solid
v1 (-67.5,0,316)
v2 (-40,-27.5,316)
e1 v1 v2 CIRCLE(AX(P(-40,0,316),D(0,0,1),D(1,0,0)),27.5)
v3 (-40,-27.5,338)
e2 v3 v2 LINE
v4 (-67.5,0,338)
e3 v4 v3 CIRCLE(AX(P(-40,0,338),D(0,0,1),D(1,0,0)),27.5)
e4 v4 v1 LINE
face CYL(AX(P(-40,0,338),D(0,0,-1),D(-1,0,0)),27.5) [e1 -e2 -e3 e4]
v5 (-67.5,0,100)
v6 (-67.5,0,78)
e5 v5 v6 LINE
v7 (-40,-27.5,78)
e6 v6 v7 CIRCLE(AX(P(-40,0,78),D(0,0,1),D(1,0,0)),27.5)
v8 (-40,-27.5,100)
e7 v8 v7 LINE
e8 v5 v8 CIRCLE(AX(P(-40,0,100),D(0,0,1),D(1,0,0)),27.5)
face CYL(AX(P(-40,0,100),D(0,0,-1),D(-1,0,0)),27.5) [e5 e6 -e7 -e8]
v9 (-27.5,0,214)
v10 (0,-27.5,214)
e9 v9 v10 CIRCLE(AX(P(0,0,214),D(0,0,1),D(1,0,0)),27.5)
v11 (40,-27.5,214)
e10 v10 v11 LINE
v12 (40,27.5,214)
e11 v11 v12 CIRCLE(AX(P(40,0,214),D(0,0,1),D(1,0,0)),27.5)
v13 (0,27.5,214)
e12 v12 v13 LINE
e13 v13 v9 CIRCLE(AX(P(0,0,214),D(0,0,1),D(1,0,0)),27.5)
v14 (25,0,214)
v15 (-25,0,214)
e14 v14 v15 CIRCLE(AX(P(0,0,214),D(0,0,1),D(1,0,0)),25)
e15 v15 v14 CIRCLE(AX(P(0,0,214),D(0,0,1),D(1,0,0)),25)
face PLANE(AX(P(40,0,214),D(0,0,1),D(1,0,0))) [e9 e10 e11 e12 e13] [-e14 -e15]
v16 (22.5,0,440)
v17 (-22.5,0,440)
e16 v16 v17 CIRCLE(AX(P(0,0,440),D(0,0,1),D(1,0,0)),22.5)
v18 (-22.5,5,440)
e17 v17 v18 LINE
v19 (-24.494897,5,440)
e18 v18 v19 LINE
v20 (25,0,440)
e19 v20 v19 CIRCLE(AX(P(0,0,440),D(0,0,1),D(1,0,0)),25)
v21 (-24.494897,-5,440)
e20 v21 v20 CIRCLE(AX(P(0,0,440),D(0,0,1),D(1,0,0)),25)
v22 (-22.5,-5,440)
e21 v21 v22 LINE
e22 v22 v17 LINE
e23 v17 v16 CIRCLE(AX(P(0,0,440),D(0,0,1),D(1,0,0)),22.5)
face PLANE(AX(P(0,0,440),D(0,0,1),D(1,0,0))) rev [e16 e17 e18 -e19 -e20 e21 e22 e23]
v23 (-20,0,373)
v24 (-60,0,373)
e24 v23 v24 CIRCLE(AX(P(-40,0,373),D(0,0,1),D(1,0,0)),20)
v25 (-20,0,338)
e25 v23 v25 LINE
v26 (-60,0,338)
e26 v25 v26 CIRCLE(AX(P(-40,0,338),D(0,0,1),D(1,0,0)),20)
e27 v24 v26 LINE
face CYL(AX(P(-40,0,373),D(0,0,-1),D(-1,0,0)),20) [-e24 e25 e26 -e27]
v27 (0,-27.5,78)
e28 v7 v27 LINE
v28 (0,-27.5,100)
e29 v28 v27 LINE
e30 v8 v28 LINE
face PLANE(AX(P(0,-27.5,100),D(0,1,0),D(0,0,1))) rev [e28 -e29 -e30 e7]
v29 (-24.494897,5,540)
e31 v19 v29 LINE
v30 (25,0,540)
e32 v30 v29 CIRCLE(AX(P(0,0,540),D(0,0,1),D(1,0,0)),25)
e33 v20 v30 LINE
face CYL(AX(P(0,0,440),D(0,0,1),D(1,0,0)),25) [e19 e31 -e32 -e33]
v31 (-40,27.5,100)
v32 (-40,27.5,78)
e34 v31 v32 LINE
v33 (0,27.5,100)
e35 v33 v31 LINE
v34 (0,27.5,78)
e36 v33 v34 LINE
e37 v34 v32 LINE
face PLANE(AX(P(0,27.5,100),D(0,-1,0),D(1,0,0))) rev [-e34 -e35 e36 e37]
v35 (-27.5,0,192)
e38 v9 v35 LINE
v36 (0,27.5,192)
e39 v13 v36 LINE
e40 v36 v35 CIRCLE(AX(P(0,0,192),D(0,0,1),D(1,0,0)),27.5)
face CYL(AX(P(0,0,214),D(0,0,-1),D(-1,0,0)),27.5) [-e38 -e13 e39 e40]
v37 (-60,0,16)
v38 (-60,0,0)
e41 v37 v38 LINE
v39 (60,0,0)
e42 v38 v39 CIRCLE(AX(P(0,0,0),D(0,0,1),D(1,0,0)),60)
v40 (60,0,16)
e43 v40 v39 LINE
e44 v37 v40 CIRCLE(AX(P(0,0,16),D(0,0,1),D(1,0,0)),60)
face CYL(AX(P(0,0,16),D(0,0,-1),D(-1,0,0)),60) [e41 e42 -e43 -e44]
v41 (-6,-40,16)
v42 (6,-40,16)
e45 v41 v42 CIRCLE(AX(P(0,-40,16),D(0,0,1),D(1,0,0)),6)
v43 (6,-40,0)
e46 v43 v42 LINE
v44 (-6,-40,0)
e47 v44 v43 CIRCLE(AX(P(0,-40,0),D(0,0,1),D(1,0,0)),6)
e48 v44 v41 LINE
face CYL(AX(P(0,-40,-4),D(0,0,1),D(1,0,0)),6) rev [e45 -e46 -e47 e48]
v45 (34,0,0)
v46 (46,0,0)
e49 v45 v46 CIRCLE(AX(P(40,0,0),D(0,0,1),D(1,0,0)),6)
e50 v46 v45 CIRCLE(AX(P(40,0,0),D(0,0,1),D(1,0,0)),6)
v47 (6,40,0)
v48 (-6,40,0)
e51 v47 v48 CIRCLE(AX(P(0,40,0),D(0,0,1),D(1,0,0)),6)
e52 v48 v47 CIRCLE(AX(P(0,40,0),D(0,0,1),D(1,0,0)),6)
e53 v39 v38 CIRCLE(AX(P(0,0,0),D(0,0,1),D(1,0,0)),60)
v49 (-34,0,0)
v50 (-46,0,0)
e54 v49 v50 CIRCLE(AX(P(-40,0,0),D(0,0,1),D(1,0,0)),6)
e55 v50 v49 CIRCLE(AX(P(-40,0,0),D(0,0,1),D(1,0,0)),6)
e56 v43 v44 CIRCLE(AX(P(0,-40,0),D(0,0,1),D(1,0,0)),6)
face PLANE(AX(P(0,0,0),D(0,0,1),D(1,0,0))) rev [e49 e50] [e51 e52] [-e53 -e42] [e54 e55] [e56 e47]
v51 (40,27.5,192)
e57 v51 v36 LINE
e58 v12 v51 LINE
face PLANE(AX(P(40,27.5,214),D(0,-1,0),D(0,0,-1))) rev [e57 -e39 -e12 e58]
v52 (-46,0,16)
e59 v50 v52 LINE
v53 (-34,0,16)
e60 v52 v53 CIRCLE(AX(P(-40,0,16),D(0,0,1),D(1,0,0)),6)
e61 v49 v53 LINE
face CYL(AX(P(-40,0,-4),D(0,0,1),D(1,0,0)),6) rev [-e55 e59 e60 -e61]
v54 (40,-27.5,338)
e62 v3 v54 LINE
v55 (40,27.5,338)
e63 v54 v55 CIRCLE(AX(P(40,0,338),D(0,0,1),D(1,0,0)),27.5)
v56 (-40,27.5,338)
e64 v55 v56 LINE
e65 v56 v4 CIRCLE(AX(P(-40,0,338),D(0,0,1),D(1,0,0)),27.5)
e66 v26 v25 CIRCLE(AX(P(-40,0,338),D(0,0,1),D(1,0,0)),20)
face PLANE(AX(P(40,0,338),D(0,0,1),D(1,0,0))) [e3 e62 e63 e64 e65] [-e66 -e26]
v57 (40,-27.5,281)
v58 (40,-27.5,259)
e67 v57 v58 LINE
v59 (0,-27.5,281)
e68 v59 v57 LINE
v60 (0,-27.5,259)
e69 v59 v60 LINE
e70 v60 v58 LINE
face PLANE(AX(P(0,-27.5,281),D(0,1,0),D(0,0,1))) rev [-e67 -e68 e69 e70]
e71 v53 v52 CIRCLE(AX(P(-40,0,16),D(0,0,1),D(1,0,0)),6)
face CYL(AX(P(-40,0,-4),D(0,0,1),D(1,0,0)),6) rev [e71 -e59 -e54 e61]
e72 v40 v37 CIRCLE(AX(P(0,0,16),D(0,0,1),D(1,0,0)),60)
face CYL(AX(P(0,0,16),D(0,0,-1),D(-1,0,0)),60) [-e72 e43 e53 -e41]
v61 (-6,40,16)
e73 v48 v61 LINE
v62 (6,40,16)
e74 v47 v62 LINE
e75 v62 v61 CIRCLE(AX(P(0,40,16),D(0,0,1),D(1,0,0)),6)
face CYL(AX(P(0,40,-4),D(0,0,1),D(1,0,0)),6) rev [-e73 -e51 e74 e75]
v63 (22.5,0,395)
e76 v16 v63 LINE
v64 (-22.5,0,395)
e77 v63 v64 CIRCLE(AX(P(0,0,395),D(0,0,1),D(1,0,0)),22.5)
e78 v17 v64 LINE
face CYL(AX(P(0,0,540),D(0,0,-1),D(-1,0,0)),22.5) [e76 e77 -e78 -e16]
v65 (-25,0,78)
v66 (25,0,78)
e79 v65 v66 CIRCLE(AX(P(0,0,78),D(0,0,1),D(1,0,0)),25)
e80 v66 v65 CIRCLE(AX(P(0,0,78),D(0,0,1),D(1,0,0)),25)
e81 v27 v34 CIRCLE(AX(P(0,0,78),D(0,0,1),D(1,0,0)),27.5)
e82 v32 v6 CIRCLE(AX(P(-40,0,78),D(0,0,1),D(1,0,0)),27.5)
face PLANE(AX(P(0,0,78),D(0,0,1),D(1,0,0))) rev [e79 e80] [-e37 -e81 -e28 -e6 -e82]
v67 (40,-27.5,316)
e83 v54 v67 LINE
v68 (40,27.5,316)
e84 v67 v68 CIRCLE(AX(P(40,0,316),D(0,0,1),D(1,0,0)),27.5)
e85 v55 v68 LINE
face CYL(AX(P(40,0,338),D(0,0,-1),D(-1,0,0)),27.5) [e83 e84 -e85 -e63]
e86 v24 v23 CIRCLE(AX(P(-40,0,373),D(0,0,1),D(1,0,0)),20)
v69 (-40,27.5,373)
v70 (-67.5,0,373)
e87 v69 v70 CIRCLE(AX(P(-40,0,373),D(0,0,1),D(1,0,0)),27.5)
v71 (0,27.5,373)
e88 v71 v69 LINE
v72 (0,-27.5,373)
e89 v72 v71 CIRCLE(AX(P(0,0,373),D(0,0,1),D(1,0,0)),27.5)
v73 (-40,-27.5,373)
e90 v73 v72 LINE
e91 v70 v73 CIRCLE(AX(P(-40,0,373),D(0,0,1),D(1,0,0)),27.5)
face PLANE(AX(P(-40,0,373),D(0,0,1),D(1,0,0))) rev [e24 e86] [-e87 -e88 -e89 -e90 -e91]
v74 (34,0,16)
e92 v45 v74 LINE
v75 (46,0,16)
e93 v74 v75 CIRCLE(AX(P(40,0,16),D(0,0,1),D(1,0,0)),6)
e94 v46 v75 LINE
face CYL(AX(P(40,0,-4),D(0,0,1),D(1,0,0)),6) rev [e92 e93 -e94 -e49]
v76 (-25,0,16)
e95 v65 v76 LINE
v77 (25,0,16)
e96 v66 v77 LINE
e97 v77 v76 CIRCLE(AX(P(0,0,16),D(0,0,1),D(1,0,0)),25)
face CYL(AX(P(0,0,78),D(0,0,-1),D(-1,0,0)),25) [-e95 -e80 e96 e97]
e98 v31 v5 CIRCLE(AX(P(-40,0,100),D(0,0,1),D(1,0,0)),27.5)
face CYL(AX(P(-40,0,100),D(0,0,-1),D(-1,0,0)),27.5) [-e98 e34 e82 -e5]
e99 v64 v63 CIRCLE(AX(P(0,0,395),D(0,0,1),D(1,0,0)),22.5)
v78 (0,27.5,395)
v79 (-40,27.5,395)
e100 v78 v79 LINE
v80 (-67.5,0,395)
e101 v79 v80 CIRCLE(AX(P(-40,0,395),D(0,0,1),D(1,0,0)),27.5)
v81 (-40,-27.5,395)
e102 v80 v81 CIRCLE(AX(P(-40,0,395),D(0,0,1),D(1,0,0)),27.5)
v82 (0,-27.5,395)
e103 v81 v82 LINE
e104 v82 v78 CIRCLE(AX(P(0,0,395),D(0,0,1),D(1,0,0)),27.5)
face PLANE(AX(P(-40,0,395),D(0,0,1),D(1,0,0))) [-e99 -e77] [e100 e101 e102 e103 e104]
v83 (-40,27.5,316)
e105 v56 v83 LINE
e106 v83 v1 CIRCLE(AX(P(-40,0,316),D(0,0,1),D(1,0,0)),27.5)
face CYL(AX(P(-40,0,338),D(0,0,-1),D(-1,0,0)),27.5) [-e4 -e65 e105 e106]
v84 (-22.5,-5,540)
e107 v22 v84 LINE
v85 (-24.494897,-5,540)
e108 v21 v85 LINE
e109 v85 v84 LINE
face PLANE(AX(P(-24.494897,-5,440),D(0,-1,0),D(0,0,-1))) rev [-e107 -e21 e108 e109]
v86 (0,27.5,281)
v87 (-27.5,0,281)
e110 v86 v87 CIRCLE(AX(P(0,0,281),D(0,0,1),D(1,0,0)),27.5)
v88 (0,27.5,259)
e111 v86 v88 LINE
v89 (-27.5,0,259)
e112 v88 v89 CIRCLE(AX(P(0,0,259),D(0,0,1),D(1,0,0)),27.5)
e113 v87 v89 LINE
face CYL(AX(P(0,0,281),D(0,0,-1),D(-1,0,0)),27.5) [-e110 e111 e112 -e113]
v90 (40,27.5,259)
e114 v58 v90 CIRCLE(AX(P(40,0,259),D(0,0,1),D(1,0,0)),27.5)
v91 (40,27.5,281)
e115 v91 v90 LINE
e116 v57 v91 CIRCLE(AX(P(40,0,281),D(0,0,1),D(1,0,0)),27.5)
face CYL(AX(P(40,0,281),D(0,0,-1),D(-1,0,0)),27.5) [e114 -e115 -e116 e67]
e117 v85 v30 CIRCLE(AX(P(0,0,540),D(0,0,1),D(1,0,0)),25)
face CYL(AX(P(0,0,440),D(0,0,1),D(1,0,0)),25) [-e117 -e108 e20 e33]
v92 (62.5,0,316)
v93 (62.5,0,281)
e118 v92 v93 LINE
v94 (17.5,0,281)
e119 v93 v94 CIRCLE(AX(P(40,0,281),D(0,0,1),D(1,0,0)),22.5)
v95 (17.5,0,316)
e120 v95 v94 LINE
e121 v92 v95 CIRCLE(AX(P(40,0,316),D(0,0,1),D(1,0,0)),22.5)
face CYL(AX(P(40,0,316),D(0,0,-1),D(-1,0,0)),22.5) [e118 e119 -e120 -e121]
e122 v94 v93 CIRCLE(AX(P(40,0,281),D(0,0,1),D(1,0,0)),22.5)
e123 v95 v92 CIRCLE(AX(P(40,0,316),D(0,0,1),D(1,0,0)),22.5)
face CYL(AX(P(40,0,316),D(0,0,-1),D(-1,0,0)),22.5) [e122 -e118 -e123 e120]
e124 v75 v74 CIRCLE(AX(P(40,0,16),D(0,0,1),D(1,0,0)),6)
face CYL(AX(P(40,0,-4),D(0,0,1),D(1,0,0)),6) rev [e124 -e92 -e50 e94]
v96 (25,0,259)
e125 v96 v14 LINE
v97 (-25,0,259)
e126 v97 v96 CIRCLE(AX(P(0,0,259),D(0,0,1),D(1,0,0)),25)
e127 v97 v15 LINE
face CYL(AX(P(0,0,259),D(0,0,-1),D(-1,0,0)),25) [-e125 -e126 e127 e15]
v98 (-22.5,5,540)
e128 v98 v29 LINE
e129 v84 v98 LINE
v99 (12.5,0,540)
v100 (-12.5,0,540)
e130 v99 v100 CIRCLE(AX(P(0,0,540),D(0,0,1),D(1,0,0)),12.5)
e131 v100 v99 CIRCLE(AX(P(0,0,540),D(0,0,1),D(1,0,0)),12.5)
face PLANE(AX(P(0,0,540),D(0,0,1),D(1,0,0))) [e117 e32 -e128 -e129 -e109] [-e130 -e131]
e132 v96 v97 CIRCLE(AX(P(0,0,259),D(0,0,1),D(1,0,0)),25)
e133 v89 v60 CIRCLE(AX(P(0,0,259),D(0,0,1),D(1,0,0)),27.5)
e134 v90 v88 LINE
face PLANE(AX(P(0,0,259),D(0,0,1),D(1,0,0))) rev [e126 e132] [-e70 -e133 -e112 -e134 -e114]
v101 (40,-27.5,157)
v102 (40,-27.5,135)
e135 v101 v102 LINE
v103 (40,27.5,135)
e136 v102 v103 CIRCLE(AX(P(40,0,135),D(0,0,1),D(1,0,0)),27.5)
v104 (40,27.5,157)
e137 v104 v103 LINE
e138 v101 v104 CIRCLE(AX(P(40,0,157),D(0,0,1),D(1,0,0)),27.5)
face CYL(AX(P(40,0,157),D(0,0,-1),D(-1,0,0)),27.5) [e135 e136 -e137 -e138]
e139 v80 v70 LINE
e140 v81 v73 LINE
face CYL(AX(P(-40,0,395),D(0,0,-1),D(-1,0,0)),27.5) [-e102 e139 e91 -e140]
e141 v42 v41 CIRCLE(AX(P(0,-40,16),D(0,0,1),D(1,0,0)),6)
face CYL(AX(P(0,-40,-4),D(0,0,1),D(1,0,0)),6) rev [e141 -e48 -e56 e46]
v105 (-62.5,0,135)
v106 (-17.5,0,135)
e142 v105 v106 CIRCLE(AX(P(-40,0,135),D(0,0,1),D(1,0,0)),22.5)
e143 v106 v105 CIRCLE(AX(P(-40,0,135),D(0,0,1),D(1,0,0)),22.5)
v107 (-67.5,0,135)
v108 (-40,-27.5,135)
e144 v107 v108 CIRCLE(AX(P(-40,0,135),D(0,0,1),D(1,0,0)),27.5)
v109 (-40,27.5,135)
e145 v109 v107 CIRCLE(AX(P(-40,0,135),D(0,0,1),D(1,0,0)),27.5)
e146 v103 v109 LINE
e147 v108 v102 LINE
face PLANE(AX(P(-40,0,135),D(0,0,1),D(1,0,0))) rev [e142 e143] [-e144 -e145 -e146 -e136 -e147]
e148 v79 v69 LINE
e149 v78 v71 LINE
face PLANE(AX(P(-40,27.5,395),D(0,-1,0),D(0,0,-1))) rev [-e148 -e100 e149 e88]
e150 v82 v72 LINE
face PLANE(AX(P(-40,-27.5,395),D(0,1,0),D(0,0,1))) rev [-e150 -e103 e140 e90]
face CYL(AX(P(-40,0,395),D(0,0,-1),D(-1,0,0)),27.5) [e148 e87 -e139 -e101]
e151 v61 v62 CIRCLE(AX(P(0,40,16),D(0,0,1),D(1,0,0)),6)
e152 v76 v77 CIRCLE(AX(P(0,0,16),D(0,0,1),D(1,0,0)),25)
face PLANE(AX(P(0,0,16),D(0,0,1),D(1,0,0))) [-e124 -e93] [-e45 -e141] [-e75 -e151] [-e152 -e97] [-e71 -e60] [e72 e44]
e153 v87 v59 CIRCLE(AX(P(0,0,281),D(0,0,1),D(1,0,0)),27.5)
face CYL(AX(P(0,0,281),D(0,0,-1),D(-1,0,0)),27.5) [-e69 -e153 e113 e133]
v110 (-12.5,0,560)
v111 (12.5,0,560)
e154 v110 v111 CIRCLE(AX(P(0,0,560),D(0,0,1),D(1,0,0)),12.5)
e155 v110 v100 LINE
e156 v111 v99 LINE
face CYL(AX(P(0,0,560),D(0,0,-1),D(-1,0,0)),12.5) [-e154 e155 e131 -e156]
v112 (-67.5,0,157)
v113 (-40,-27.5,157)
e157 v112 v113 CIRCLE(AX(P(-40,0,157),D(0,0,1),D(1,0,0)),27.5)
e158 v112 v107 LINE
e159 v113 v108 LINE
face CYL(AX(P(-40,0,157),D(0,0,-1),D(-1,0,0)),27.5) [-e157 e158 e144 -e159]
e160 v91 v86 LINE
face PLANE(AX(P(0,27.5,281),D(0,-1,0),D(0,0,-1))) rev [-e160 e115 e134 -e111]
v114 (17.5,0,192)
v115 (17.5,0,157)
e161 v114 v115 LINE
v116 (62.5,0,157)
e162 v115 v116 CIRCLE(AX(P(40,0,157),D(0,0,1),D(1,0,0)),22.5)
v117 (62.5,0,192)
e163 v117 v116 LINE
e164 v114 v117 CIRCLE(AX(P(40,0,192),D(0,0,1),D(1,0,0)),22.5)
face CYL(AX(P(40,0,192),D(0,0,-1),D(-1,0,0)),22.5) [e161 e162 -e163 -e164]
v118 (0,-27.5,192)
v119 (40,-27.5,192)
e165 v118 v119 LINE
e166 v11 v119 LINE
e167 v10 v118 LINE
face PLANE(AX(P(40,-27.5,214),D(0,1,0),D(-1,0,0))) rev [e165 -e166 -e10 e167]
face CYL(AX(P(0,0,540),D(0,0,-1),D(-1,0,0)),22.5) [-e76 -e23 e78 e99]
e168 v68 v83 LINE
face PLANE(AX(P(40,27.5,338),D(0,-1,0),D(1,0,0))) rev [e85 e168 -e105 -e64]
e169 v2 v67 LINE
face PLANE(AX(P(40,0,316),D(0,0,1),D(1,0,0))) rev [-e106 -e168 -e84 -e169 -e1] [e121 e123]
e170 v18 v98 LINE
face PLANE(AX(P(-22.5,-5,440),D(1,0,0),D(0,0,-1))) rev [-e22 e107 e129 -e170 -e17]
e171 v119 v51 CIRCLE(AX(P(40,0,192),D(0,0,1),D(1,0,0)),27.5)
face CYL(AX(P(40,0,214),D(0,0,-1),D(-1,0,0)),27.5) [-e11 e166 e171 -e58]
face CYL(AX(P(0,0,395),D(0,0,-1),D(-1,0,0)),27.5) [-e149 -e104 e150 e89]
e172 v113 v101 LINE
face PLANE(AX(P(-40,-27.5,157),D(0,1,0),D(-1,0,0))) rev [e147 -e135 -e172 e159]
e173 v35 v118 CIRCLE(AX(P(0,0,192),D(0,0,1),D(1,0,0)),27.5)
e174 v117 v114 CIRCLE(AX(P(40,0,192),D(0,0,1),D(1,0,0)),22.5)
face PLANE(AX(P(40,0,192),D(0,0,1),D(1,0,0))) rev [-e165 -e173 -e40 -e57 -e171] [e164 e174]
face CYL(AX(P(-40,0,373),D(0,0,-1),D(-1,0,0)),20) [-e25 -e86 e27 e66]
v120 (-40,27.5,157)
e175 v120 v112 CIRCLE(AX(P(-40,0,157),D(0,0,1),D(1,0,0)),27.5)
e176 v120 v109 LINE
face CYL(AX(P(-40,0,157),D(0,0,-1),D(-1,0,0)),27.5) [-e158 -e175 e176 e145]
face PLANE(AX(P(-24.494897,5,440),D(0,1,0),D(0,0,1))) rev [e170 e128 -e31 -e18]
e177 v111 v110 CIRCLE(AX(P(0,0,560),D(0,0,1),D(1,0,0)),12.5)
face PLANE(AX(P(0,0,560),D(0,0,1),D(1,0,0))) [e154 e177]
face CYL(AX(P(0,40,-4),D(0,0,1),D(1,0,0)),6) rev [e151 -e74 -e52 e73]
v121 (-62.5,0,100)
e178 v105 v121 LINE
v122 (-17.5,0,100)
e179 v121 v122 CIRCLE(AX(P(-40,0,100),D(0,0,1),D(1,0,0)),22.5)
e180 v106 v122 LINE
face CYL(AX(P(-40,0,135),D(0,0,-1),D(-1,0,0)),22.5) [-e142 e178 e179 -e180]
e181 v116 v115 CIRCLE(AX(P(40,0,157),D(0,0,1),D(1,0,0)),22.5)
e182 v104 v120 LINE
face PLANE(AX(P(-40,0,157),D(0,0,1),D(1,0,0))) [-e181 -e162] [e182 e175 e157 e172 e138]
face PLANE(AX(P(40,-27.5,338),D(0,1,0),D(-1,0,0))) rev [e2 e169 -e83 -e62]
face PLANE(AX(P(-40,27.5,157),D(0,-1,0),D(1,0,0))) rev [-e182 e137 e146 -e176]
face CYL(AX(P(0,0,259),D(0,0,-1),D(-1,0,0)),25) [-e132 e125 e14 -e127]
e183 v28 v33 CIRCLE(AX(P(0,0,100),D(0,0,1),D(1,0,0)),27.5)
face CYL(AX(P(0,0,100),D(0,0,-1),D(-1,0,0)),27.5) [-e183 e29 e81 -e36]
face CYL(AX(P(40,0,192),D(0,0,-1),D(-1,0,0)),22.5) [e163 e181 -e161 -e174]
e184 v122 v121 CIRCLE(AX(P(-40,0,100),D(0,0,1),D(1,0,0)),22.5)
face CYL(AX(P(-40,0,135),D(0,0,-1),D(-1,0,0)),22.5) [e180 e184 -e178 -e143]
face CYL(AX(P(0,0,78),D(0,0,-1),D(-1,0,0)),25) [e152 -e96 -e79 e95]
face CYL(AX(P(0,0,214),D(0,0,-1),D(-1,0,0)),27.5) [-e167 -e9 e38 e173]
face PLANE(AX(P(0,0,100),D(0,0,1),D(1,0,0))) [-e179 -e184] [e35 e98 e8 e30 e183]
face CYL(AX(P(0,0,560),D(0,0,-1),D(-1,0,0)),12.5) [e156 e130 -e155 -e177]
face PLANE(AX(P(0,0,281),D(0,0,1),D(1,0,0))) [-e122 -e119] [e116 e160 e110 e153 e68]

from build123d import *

# Parameters (mm, degrees)
FLANGE_SKETCH_R               = 60
FLANGE_120X16_DEPTH           = 16
FRONT_SHAFT_SKETCH_R          = 25
FRONT_SHAFT_50X62_DEPTH       = 62
CRANK_WEB_1_DEPTH             = 22
CRANKPIN_1_SKETCH_R           = 22.5
CRANKPIN_1_45_DEPTH           = 35
CRANK_WEB_2_DEPTH             = 22
CRANKPIN_2_SKETCH_R           = 22.5
CRANKPIN_2_45_DEPTH           = 35
CRANK_WEB_3_DEPTH             = 22
CENTRE_MAIN_JOURNAL_SKETCH_R  = 25
CENTRE_MAIN_JOURNAL_50_DEPTH  = 45
CRANK_WEB_4_DEPTH             = 22
CRANKPIN_3_SKETCH_R           = 22.5
CRANKPIN_3_45_DEPTH           = 35
CRANK_WEB_5_DEPTH             = 22
CRANKPIN_4_SKETCH_R           = 20
CRANKPIN_4_40_DEPTH           = 35
CRANK_WEB_6_DEPTH             = 22
REAR_SHAFT_SKETCH_R           = 22.5
REAR_SHAFT_45X145_DEPTH       = 145
REAR_START                    = -100
REAR_SHAFT_STEP_SKETCH_R      = 25
REAR_SHAFT_STEP_50X100_DEPTH  = 100
REAR_SHAFT_PROFILE_CUT_DEPTH  = 100
END_STUB_SKETCH_R             = 12.5
END_STUB_25X20_DEPTH          = 20
FLANGE_BOLT_HOLES_SKETCH_R    = 6
FLANGE_BOLT_HOLES_4X_12_DEPTH = 20


with BuildPart() as part:
    # Flange Sketch → Flange Ø120x16 (new body)
    with BuildSketch(Plane.XY):
        Circle(FLANGE_SKETCH_R)
    extrude(amount=FLANGE_120X16_DEPTH)

    # Front Shaft Sketch → Front Shaft Ø50x62 (add)
    with BuildSketch(Plane.XY.offset(16)):
        Circle(FRONT_SHAFT_SKETCH_R)
    extrude(amount=FRONT_SHAFT_50X62_DEPTH)

    # Crank Web 1 Sketch → Crank Web 1 (add)
    with BuildSketch(Plane.XY.offset(78)):
        with BuildLine():
            Line((0, -27.5), (-40, -27.5))
            ThreePointArc((-40, -27.5), (-67.5, 0), (-40, 27.5))
            Line((-40, 27.5), (0, 27.5))
            ThreePointArc((0, 27.5), (27.5, 0), (0, -27.5))
        make_face()
    extrude(amount=CRANK_WEB_1_DEPTH)

    # Crankpin 1 Sketch → Crankpin 1 Ø45 (add)
    with BuildSketch(Plane.XY.offset(100)):
        with Locations((-40, 0)):
            Circle(CRANKPIN_1_SKETCH_R)
    extrude(amount=CRANKPIN_1_45_DEPTH)

    # Crank Web 2 Sketch → Crank Web 2 (add)
    with BuildSketch(Plane.XY.offset(135)):
        with BuildLine():
            Line((-40, 27.5), (40, 27.5))
            ThreePointArc((40, 27.5), (67.5, 0), (40, -27.5))
            Line((40, -27.5), (-40, -27.5))
            ThreePointArc((-40, -27.5), (-67.5, 0), (-40, 27.5))
        make_face()
    extrude(amount=CRANK_WEB_2_DEPTH)

    # Crankpin 2 Sketch → Crankpin 2 Ø45 (add)
    with BuildSketch(Plane.XY.offset(157)):
        with Locations((40, 0)):
            Circle(CRANKPIN_2_SKETCH_R)
    extrude(amount=CRANKPIN_2_45_DEPTH)

    # Crank Web 3 Sketch → Crank Web 3 (add)
    with BuildSketch(Plane.XY.offset(192)):
        with BuildLine():
            Line((40, -27.5), (0, -27.5))
            ThreePointArc((0, -27.5), (-27.5, 0), (0, 27.5))
            Line((0, 27.5), (40, 27.5))
            ThreePointArc((40, 27.5), (67.5, 0), (40, -27.5))
        make_face()
    extrude(amount=CRANK_WEB_3_DEPTH)

    # Centre Main Journal Sketch → Centre Main Journal Ø50 (add)
    with BuildSketch(Plane.XY.offset(214)):
        Circle(CENTRE_MAIN_JOURNAL_SKETCH_R)
    extrude(amount=CENTRE_MAIN_JOURNAL_50_DEPTH)

    # Crank Web 4 Sketch → Crank Web 4 (add)
    with BuildSketch(Plane.XY.offset(259)):
        with BuildLine():
            Line((0, 27.5), (40, 27.5))
            ThreePointArc((40, 27.5), (67.5, 0), (40, -27.5))
            Line((40, -27.5), (0, -27.5))
            ThreePointArc((0, -27.5), (-27.5, 0), (0, 27.5))
        make_face()
    extrude(amount=CRANK_WEB_4_DEPTH)

    # Crankpin 3 Sketch → Crankpin 3 Ø45 (add)
    with BuildSketch(Plane.XY.offset(281)):
        with Locations((40, 0)):
            Circle(CRANKPIN_3_SKETCH_R)
    extrude(amount=CRANKPIN_3_45_DEPTH)

    # Crank Web 5 Sketch → Crank Web 5 (add)
    with BuildSketch(Plane.XY.offset(316)):
        with BuildLine():
            Line((40, -27.5), (-40, -27.5))
            ThreePointArc((-40, -27.5), (-67.5, 0), (-40, 27.5))
            Line((-40, 27.5), (40, 27.5))
            ThreePointArc((40, 27.5), (67.5, 0), (40, -27.5))
        make_face()
    extrude(amount=CRANK_WEB_5_DEPTH)

    # Crankpin 4 Sketch → Crankpin 4 Ø40 (add)
    with BuildSketch(Plane.XY.offset(338)):
        with Locations((-40, 0)):
            Circle(CRANKPIN_4_SKETCH_R)
    extrude(amount=CRANKPIN_4_40_DEPTH)

    # Crank Web 6 Sketch → Crank Web 6 (add)
    with BuildSketch(Plane.XY.offset(373)):
        with BuildLine():
            Line((-40, 27.5), (0, 27.5))
            ThreePointArc((0, 27.5), (27.5, 0), (0, -27.5))
            Line((0, -27.5), (-40, -27.5))
            ThreePointArc((-40, -27.5), (-67.5, 0), (-40, 27.5))
        make_face()
    extrude(amount=CRANK_WEB_6_DEPTH)

    # Rear Shaft Sketch → Rear Shaft Ø45x145 (add)
    with BuildSketch(Plane.XY.offset(395)):
        Circle(REAR_SHAFT_SKETCH_R)
    extrude(amount=REAR_SHAFT_45X145_DEPTH)

    # Rear Shaft Step Sketch → Rear Shaft Step Ø50x100 (add)
    with BuildSketch(Plane.XY.offset(540).offset(REAR_START)):
        Circle(REAR_SHAFT_STEP_SKETCH_R)
    extrude(amount=REAR_SHAFT_STEP_50X100_DEPTH)

    # Rear Shaft Cut Sketch → Rear Shaft Profile Cut (cut)
    with BuildSketch(Plane.XY.offset(540).offset(REAR_START)):
        with BuildLine():
            Line((-24.494897428, -5), (-22.5, -5))
            Line((-22.5, -5), (-22.5, 5))
            Line((-22.5, 5), (-24.494897428, 5))
            ThreePointArc((-24.494897428, 5), (-25, 0), (-24.494897428, -5))
        make_face()
    extrude(amount=REAR_SHAFT_PROFILE_CUT_DEPTH, mode=Mode.SUBTRACT)

    # End Stub Sketch → End Stub Ø25x20 (add)
    with BuildSketch(Plane.XY.offset(540)):
        Circle(END_STUB_SKETCH_R)
    extrude(amount=END_STUB_25X20_DEPTH)

    # Flange Bolt Holes Sketch → Flange Bolt Holes 4xØ12 (cut)
    with BuildSketch(Plane.XY.offset(16)):
        with Locations((0, 40)):
            Circle(FLANGE_BOLT_HOLES_SKETCH_R)
        with Locations((0, -40)):
            Circle(FLANGE_BOLT_HOLES_SKETCH_R)
        with Locations((-40, 0)):
            Circle(FLANGE_BOLT_HOLES_SKETCH_R)
        with Locations((40, 0)):
            Circle(FLANGE_BOLT_HOLES_SKETCH_R)
    extrude(amount=-FLANGE_BOLT_HOLES_4X_12_DEPTH, mode=Mode.SUBTRACT)


solid = part.part
